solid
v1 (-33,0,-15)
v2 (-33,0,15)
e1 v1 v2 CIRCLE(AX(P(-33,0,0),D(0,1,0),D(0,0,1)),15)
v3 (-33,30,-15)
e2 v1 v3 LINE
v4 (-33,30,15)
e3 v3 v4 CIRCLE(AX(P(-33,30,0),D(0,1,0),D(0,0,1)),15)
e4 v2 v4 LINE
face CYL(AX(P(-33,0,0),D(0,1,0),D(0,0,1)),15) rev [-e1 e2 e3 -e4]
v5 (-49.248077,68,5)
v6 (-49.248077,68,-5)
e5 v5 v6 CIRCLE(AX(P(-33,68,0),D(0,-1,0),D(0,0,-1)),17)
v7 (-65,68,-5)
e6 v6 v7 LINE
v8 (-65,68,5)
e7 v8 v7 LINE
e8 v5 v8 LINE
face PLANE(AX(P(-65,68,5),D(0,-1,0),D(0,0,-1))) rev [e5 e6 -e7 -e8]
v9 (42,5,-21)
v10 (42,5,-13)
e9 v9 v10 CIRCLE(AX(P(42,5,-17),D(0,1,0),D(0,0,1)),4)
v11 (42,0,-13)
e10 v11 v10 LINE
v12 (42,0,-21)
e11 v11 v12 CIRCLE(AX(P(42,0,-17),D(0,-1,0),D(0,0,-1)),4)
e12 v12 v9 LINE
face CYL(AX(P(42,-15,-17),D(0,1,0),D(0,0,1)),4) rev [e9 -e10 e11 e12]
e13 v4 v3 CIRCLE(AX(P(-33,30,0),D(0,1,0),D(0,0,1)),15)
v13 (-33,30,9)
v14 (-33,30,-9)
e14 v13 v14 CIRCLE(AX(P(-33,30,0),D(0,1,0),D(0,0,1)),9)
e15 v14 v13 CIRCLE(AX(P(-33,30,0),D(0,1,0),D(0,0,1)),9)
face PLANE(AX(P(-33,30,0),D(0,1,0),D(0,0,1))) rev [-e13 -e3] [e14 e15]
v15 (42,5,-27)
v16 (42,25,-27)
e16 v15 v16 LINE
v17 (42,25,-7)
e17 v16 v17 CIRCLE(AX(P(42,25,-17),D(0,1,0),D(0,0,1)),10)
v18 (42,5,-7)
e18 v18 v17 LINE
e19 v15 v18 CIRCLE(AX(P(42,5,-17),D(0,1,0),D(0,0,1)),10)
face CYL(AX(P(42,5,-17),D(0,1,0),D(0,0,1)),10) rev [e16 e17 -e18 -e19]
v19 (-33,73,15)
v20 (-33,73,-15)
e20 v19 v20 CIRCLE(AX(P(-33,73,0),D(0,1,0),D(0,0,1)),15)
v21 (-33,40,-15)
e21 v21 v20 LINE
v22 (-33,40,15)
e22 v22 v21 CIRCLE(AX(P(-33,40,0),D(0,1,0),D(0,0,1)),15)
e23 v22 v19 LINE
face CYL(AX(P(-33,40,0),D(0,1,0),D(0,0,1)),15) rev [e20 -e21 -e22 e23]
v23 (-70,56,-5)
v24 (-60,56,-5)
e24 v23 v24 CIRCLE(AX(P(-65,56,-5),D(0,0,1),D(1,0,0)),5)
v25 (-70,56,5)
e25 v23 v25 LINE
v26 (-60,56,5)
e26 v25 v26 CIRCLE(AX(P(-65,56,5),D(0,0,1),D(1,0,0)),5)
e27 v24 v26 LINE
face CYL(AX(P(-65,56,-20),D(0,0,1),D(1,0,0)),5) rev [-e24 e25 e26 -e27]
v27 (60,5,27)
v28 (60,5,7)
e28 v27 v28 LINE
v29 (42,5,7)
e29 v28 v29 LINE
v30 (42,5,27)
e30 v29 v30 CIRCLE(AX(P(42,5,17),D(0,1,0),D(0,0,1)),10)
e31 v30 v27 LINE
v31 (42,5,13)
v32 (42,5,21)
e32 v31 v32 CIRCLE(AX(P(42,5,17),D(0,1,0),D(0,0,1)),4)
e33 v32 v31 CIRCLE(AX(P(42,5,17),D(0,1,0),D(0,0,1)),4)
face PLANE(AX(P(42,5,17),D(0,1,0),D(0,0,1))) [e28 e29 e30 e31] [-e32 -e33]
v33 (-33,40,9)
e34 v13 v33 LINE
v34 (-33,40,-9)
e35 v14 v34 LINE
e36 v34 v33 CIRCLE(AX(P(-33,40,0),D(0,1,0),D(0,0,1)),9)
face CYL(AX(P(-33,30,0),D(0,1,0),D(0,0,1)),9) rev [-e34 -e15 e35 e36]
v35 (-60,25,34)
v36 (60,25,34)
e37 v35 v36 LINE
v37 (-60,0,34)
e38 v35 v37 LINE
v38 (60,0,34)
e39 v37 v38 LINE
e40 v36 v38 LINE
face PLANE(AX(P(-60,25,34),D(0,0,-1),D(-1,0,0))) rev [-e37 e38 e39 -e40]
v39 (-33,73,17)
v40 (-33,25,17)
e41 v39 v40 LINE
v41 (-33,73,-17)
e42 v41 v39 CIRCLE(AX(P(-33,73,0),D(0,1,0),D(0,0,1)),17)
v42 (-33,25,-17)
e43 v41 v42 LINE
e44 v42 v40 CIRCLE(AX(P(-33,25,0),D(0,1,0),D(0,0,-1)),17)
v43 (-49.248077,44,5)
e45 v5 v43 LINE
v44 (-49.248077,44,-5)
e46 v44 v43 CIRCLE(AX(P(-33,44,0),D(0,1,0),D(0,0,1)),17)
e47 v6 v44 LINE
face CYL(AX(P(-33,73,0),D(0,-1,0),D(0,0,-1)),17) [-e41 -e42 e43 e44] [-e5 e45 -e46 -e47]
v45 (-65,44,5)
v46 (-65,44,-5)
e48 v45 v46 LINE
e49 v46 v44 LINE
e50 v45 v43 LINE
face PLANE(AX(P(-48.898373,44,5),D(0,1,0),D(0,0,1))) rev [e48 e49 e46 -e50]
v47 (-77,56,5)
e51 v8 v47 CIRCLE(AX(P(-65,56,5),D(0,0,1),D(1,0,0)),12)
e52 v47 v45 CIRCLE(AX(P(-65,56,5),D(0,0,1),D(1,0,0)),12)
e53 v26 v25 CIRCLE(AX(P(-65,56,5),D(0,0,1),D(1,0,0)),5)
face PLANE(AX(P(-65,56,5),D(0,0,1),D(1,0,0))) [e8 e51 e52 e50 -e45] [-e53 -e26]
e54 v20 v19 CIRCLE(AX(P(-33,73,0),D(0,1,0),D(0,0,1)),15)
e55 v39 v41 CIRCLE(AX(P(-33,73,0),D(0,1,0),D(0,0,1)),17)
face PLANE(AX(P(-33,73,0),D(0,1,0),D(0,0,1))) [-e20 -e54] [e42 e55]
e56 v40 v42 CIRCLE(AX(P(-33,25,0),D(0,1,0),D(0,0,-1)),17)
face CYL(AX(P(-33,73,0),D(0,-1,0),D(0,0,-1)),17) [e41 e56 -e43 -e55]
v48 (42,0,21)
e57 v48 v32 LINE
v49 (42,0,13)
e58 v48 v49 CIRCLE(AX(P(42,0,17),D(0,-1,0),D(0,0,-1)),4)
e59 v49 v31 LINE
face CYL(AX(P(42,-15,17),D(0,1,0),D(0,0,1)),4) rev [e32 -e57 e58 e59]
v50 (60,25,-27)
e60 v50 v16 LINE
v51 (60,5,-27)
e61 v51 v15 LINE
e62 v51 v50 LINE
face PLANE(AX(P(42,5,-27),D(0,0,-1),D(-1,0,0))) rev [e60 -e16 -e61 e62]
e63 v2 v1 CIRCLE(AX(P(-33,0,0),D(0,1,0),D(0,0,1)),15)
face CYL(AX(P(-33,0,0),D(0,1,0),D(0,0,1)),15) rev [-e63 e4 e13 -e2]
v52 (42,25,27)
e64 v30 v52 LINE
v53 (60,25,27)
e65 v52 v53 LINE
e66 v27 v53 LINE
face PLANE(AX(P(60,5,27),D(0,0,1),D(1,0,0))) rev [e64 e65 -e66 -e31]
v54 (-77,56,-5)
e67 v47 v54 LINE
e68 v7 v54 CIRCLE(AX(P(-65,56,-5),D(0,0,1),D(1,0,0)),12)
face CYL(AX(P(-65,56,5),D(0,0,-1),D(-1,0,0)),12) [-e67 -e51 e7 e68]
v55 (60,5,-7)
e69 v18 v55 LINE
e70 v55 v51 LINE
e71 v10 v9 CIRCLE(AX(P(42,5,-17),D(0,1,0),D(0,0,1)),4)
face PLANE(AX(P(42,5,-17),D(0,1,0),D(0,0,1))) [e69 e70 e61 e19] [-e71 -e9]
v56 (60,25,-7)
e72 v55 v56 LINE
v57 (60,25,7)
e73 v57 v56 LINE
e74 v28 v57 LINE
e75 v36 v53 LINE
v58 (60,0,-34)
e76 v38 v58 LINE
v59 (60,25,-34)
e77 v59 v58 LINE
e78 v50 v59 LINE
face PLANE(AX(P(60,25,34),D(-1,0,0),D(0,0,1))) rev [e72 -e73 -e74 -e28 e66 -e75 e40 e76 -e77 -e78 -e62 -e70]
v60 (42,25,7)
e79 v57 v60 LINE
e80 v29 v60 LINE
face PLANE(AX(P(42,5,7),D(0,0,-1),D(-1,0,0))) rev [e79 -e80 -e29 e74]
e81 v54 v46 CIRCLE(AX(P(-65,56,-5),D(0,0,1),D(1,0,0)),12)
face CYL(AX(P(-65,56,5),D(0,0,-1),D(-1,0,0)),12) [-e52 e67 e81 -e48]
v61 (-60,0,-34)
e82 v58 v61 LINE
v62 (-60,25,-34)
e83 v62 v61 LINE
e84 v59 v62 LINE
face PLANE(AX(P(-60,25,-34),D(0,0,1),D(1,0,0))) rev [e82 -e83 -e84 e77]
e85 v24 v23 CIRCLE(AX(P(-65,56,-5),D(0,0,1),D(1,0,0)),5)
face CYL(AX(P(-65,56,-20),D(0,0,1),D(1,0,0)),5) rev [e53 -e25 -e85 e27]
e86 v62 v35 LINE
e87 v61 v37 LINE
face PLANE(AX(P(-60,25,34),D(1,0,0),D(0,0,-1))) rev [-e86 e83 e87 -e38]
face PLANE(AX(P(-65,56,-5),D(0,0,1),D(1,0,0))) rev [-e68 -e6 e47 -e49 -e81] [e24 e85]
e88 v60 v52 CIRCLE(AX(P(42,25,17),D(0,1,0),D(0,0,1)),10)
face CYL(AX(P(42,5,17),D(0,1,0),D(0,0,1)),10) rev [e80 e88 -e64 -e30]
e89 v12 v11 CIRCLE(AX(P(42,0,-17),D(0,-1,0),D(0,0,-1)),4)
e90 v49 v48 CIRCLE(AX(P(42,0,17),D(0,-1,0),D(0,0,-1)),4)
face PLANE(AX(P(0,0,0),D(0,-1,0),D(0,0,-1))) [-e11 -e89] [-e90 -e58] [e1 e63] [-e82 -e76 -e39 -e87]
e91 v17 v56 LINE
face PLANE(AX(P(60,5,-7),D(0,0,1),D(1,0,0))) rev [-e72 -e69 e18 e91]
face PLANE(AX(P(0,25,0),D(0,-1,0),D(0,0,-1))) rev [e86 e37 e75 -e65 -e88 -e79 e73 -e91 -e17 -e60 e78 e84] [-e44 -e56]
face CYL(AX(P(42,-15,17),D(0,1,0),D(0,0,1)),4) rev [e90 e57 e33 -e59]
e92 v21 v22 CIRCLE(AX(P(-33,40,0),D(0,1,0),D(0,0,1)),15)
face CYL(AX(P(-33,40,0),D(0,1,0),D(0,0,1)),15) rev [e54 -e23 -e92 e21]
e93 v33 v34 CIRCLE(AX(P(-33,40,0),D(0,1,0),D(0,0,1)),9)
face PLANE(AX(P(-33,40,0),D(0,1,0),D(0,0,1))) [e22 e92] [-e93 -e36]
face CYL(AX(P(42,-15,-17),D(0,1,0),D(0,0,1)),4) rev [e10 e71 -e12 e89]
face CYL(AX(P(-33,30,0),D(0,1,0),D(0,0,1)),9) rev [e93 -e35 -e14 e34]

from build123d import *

# Parameters (mm, degrees)
BASE_PLATE_SKETCH_W       = 120
BASE_PLATE_SKETCH_H       = 68
BASE_PLATE_DEPTH          = 25
HUB_SKETCH_R              = 17
HUB_34_DEPTH              = 48
LUG_DEPTH                 = 5
HUB_BORE_SKETCH_R         = 15
HUB_BORE_30_DEPTH         = 33
THROUGH_HOLE_SKETCH_R     = 9
THROUGH_HOLE_18_DEPTH     = 10
BOTTOM_BORE_SKETCH_R      = 15
BOTTOM_BORE_30_DEPTH      = 95.519839187
LUG_HOLE_SKETCH_R         = 5
LUG_HOLE_10_DEPTH         = 25
MOUNTING_SLOTS_2X20_DEPTH = 20
SLOT_RELIEF_SKETCH_R      = 4
SLOT_RELIEF_CUTS_DEPTH    = 20


with BuildPart() as part:
    # Base Plate Sketch → Base Plate (new body)
    with BuildSketch(Plane(origin=(0, 0, 0), x_dir=(1, 0, 0), z_dir=(0, 1, 0))):
        Rectangle(BASE_PLATE_SKETCH_W, BASE_PLATE_SKETCH_H)
    extrude(amount=BASE_PLATE_DEPTH)

    # Hub Sketch → Hub Ø34 (add)
    with BuildSketch(Plane(origin=(0, 25, 0), x_dir=(1, 0, 0), z_dir=(0, 1, 0))):
        with Locations(Location((-33, 0, 0), (0, 0, 90))):
            Circle(HUB_SKETCH_R)
    extrude(amount=HUB_34_DEPTH)

    # Lug Sketch → Lug (add, symmetric)
    with BuildSketch(Plane.XY):
        with BuildLine():
            Line((-65, 68), (-48.898372545, 68))
            Line((-48.898372545, 68), (-48.898372545, 44))
            Line((-48.898372545, 44), (-65, 44))
            ThreePointArc((-65, 44), (-77, 56), (-65, 68))
        make_face()
    extrude(amount=LUG_DEPTH, both=True)

    # Hub Bore Sketch → Hub Bore Ø30 (cut)
    with BuildSketch(Plane(origin=(0, 73, 0), x_dir=(1, 0, 0), z_dir=(0, 1, 0))):
        with Locations(Location((-33, 0, 0), (0, 0, 270))):
            Circle(HUB_BORE_SKETCH_R)
    extrude(amount=-HUB_BORE_30_DEPTH, mode=Mode.SUBTRACT)

    # Through Hole Sketch → Through Hole Ø18 (cut)
    with BuildSketch(Plane(origin=(0, 40, 0), x_dir=(1, 0, 0), z_dir=(0, 1, 0))):
        with Locations(Location((-33, 0, 0), (0, 0, 270))):
            Circle(THROUGH_HOLE_SKETCH_R)
    extrude(amount=-THROUGH_HOLE_18_DEPTH, mode=Mode.SUBTRACT)

    # Bottom Bore Sketch → Bottom Bore Ø30 (cut, through all)
    with BuildSketch(Plane(origin=(0, 30, 0), x_dir=(1, 0, 0), z_dir=(0, 1, 0))):
        with Locations(Location((-33, 0, 0), (0, 0, 270))):
            Circle(BOTTOM_BORE_SKETCH_R)
    extrude(amount=-BOTTOM_BORE_30_DEPTH, mode=Mode.SUBTRACT)

    # Lug Hole Sketch → Lug Hole Ø10 (cut)
    with BuildSketch(Plane.XY.offset(5)):
        with Locations((-65, 56)):
            Circle(LUG_HOLE_SKETCH_R)
    extrude(amount=-LUG_HOLE_10_DEPTH, mode=Mode.SUBTRACT)

    # Mounting Slots Sketch → Mounting Slots 2x20 (cut)
    with BuildSketch(Plane(origin=(0, 25, 0), x_dir=(1, 0, 0), z_dir=(0, 1, 0))):
        with BuildLine():
            Line((42, 27), (60, 27))
            Line((60, 27), (60, 7))
            Line((60, 7), (42, 7))
            ThreePointArc((42, 7), (32, 17), (42, 27))
        make_face()
        with BuildLine():
            Line((42, -7), (60, -7))
            Line((60, -7), (60, -27))
            Line((60, -27), (42, -27))
            ThreePointArc((42, -27), (32, -17), (42, -7))
        make_face()
    extrude(amount=-MOUNTING_SLOTS_2X20_DEPTH, mode=Mode.SUBTRACT)

    # Slot Relief Sketch → Slot Relief Cuts (cut)
    with BuildSketch(Plane(origin=(0, 5, 0), x_dir=(1, 0, 0), z_dir=(0, 1, 0))):
        with Locations(Location((42, 17, 0), (0, 0, 270))):
            Circle(SLOT_RELIEF_SKETCH_R)
        with Locations(Location((42, -17, 0), (0, 0, 270))):
            Circle(SLOT_RELIEF_SKETCH_R)
    extrude(amount=-SLOT_RELIEF_CUTS_DEPTH, mode=Mode.SUBTRACT)


solid = part.part
